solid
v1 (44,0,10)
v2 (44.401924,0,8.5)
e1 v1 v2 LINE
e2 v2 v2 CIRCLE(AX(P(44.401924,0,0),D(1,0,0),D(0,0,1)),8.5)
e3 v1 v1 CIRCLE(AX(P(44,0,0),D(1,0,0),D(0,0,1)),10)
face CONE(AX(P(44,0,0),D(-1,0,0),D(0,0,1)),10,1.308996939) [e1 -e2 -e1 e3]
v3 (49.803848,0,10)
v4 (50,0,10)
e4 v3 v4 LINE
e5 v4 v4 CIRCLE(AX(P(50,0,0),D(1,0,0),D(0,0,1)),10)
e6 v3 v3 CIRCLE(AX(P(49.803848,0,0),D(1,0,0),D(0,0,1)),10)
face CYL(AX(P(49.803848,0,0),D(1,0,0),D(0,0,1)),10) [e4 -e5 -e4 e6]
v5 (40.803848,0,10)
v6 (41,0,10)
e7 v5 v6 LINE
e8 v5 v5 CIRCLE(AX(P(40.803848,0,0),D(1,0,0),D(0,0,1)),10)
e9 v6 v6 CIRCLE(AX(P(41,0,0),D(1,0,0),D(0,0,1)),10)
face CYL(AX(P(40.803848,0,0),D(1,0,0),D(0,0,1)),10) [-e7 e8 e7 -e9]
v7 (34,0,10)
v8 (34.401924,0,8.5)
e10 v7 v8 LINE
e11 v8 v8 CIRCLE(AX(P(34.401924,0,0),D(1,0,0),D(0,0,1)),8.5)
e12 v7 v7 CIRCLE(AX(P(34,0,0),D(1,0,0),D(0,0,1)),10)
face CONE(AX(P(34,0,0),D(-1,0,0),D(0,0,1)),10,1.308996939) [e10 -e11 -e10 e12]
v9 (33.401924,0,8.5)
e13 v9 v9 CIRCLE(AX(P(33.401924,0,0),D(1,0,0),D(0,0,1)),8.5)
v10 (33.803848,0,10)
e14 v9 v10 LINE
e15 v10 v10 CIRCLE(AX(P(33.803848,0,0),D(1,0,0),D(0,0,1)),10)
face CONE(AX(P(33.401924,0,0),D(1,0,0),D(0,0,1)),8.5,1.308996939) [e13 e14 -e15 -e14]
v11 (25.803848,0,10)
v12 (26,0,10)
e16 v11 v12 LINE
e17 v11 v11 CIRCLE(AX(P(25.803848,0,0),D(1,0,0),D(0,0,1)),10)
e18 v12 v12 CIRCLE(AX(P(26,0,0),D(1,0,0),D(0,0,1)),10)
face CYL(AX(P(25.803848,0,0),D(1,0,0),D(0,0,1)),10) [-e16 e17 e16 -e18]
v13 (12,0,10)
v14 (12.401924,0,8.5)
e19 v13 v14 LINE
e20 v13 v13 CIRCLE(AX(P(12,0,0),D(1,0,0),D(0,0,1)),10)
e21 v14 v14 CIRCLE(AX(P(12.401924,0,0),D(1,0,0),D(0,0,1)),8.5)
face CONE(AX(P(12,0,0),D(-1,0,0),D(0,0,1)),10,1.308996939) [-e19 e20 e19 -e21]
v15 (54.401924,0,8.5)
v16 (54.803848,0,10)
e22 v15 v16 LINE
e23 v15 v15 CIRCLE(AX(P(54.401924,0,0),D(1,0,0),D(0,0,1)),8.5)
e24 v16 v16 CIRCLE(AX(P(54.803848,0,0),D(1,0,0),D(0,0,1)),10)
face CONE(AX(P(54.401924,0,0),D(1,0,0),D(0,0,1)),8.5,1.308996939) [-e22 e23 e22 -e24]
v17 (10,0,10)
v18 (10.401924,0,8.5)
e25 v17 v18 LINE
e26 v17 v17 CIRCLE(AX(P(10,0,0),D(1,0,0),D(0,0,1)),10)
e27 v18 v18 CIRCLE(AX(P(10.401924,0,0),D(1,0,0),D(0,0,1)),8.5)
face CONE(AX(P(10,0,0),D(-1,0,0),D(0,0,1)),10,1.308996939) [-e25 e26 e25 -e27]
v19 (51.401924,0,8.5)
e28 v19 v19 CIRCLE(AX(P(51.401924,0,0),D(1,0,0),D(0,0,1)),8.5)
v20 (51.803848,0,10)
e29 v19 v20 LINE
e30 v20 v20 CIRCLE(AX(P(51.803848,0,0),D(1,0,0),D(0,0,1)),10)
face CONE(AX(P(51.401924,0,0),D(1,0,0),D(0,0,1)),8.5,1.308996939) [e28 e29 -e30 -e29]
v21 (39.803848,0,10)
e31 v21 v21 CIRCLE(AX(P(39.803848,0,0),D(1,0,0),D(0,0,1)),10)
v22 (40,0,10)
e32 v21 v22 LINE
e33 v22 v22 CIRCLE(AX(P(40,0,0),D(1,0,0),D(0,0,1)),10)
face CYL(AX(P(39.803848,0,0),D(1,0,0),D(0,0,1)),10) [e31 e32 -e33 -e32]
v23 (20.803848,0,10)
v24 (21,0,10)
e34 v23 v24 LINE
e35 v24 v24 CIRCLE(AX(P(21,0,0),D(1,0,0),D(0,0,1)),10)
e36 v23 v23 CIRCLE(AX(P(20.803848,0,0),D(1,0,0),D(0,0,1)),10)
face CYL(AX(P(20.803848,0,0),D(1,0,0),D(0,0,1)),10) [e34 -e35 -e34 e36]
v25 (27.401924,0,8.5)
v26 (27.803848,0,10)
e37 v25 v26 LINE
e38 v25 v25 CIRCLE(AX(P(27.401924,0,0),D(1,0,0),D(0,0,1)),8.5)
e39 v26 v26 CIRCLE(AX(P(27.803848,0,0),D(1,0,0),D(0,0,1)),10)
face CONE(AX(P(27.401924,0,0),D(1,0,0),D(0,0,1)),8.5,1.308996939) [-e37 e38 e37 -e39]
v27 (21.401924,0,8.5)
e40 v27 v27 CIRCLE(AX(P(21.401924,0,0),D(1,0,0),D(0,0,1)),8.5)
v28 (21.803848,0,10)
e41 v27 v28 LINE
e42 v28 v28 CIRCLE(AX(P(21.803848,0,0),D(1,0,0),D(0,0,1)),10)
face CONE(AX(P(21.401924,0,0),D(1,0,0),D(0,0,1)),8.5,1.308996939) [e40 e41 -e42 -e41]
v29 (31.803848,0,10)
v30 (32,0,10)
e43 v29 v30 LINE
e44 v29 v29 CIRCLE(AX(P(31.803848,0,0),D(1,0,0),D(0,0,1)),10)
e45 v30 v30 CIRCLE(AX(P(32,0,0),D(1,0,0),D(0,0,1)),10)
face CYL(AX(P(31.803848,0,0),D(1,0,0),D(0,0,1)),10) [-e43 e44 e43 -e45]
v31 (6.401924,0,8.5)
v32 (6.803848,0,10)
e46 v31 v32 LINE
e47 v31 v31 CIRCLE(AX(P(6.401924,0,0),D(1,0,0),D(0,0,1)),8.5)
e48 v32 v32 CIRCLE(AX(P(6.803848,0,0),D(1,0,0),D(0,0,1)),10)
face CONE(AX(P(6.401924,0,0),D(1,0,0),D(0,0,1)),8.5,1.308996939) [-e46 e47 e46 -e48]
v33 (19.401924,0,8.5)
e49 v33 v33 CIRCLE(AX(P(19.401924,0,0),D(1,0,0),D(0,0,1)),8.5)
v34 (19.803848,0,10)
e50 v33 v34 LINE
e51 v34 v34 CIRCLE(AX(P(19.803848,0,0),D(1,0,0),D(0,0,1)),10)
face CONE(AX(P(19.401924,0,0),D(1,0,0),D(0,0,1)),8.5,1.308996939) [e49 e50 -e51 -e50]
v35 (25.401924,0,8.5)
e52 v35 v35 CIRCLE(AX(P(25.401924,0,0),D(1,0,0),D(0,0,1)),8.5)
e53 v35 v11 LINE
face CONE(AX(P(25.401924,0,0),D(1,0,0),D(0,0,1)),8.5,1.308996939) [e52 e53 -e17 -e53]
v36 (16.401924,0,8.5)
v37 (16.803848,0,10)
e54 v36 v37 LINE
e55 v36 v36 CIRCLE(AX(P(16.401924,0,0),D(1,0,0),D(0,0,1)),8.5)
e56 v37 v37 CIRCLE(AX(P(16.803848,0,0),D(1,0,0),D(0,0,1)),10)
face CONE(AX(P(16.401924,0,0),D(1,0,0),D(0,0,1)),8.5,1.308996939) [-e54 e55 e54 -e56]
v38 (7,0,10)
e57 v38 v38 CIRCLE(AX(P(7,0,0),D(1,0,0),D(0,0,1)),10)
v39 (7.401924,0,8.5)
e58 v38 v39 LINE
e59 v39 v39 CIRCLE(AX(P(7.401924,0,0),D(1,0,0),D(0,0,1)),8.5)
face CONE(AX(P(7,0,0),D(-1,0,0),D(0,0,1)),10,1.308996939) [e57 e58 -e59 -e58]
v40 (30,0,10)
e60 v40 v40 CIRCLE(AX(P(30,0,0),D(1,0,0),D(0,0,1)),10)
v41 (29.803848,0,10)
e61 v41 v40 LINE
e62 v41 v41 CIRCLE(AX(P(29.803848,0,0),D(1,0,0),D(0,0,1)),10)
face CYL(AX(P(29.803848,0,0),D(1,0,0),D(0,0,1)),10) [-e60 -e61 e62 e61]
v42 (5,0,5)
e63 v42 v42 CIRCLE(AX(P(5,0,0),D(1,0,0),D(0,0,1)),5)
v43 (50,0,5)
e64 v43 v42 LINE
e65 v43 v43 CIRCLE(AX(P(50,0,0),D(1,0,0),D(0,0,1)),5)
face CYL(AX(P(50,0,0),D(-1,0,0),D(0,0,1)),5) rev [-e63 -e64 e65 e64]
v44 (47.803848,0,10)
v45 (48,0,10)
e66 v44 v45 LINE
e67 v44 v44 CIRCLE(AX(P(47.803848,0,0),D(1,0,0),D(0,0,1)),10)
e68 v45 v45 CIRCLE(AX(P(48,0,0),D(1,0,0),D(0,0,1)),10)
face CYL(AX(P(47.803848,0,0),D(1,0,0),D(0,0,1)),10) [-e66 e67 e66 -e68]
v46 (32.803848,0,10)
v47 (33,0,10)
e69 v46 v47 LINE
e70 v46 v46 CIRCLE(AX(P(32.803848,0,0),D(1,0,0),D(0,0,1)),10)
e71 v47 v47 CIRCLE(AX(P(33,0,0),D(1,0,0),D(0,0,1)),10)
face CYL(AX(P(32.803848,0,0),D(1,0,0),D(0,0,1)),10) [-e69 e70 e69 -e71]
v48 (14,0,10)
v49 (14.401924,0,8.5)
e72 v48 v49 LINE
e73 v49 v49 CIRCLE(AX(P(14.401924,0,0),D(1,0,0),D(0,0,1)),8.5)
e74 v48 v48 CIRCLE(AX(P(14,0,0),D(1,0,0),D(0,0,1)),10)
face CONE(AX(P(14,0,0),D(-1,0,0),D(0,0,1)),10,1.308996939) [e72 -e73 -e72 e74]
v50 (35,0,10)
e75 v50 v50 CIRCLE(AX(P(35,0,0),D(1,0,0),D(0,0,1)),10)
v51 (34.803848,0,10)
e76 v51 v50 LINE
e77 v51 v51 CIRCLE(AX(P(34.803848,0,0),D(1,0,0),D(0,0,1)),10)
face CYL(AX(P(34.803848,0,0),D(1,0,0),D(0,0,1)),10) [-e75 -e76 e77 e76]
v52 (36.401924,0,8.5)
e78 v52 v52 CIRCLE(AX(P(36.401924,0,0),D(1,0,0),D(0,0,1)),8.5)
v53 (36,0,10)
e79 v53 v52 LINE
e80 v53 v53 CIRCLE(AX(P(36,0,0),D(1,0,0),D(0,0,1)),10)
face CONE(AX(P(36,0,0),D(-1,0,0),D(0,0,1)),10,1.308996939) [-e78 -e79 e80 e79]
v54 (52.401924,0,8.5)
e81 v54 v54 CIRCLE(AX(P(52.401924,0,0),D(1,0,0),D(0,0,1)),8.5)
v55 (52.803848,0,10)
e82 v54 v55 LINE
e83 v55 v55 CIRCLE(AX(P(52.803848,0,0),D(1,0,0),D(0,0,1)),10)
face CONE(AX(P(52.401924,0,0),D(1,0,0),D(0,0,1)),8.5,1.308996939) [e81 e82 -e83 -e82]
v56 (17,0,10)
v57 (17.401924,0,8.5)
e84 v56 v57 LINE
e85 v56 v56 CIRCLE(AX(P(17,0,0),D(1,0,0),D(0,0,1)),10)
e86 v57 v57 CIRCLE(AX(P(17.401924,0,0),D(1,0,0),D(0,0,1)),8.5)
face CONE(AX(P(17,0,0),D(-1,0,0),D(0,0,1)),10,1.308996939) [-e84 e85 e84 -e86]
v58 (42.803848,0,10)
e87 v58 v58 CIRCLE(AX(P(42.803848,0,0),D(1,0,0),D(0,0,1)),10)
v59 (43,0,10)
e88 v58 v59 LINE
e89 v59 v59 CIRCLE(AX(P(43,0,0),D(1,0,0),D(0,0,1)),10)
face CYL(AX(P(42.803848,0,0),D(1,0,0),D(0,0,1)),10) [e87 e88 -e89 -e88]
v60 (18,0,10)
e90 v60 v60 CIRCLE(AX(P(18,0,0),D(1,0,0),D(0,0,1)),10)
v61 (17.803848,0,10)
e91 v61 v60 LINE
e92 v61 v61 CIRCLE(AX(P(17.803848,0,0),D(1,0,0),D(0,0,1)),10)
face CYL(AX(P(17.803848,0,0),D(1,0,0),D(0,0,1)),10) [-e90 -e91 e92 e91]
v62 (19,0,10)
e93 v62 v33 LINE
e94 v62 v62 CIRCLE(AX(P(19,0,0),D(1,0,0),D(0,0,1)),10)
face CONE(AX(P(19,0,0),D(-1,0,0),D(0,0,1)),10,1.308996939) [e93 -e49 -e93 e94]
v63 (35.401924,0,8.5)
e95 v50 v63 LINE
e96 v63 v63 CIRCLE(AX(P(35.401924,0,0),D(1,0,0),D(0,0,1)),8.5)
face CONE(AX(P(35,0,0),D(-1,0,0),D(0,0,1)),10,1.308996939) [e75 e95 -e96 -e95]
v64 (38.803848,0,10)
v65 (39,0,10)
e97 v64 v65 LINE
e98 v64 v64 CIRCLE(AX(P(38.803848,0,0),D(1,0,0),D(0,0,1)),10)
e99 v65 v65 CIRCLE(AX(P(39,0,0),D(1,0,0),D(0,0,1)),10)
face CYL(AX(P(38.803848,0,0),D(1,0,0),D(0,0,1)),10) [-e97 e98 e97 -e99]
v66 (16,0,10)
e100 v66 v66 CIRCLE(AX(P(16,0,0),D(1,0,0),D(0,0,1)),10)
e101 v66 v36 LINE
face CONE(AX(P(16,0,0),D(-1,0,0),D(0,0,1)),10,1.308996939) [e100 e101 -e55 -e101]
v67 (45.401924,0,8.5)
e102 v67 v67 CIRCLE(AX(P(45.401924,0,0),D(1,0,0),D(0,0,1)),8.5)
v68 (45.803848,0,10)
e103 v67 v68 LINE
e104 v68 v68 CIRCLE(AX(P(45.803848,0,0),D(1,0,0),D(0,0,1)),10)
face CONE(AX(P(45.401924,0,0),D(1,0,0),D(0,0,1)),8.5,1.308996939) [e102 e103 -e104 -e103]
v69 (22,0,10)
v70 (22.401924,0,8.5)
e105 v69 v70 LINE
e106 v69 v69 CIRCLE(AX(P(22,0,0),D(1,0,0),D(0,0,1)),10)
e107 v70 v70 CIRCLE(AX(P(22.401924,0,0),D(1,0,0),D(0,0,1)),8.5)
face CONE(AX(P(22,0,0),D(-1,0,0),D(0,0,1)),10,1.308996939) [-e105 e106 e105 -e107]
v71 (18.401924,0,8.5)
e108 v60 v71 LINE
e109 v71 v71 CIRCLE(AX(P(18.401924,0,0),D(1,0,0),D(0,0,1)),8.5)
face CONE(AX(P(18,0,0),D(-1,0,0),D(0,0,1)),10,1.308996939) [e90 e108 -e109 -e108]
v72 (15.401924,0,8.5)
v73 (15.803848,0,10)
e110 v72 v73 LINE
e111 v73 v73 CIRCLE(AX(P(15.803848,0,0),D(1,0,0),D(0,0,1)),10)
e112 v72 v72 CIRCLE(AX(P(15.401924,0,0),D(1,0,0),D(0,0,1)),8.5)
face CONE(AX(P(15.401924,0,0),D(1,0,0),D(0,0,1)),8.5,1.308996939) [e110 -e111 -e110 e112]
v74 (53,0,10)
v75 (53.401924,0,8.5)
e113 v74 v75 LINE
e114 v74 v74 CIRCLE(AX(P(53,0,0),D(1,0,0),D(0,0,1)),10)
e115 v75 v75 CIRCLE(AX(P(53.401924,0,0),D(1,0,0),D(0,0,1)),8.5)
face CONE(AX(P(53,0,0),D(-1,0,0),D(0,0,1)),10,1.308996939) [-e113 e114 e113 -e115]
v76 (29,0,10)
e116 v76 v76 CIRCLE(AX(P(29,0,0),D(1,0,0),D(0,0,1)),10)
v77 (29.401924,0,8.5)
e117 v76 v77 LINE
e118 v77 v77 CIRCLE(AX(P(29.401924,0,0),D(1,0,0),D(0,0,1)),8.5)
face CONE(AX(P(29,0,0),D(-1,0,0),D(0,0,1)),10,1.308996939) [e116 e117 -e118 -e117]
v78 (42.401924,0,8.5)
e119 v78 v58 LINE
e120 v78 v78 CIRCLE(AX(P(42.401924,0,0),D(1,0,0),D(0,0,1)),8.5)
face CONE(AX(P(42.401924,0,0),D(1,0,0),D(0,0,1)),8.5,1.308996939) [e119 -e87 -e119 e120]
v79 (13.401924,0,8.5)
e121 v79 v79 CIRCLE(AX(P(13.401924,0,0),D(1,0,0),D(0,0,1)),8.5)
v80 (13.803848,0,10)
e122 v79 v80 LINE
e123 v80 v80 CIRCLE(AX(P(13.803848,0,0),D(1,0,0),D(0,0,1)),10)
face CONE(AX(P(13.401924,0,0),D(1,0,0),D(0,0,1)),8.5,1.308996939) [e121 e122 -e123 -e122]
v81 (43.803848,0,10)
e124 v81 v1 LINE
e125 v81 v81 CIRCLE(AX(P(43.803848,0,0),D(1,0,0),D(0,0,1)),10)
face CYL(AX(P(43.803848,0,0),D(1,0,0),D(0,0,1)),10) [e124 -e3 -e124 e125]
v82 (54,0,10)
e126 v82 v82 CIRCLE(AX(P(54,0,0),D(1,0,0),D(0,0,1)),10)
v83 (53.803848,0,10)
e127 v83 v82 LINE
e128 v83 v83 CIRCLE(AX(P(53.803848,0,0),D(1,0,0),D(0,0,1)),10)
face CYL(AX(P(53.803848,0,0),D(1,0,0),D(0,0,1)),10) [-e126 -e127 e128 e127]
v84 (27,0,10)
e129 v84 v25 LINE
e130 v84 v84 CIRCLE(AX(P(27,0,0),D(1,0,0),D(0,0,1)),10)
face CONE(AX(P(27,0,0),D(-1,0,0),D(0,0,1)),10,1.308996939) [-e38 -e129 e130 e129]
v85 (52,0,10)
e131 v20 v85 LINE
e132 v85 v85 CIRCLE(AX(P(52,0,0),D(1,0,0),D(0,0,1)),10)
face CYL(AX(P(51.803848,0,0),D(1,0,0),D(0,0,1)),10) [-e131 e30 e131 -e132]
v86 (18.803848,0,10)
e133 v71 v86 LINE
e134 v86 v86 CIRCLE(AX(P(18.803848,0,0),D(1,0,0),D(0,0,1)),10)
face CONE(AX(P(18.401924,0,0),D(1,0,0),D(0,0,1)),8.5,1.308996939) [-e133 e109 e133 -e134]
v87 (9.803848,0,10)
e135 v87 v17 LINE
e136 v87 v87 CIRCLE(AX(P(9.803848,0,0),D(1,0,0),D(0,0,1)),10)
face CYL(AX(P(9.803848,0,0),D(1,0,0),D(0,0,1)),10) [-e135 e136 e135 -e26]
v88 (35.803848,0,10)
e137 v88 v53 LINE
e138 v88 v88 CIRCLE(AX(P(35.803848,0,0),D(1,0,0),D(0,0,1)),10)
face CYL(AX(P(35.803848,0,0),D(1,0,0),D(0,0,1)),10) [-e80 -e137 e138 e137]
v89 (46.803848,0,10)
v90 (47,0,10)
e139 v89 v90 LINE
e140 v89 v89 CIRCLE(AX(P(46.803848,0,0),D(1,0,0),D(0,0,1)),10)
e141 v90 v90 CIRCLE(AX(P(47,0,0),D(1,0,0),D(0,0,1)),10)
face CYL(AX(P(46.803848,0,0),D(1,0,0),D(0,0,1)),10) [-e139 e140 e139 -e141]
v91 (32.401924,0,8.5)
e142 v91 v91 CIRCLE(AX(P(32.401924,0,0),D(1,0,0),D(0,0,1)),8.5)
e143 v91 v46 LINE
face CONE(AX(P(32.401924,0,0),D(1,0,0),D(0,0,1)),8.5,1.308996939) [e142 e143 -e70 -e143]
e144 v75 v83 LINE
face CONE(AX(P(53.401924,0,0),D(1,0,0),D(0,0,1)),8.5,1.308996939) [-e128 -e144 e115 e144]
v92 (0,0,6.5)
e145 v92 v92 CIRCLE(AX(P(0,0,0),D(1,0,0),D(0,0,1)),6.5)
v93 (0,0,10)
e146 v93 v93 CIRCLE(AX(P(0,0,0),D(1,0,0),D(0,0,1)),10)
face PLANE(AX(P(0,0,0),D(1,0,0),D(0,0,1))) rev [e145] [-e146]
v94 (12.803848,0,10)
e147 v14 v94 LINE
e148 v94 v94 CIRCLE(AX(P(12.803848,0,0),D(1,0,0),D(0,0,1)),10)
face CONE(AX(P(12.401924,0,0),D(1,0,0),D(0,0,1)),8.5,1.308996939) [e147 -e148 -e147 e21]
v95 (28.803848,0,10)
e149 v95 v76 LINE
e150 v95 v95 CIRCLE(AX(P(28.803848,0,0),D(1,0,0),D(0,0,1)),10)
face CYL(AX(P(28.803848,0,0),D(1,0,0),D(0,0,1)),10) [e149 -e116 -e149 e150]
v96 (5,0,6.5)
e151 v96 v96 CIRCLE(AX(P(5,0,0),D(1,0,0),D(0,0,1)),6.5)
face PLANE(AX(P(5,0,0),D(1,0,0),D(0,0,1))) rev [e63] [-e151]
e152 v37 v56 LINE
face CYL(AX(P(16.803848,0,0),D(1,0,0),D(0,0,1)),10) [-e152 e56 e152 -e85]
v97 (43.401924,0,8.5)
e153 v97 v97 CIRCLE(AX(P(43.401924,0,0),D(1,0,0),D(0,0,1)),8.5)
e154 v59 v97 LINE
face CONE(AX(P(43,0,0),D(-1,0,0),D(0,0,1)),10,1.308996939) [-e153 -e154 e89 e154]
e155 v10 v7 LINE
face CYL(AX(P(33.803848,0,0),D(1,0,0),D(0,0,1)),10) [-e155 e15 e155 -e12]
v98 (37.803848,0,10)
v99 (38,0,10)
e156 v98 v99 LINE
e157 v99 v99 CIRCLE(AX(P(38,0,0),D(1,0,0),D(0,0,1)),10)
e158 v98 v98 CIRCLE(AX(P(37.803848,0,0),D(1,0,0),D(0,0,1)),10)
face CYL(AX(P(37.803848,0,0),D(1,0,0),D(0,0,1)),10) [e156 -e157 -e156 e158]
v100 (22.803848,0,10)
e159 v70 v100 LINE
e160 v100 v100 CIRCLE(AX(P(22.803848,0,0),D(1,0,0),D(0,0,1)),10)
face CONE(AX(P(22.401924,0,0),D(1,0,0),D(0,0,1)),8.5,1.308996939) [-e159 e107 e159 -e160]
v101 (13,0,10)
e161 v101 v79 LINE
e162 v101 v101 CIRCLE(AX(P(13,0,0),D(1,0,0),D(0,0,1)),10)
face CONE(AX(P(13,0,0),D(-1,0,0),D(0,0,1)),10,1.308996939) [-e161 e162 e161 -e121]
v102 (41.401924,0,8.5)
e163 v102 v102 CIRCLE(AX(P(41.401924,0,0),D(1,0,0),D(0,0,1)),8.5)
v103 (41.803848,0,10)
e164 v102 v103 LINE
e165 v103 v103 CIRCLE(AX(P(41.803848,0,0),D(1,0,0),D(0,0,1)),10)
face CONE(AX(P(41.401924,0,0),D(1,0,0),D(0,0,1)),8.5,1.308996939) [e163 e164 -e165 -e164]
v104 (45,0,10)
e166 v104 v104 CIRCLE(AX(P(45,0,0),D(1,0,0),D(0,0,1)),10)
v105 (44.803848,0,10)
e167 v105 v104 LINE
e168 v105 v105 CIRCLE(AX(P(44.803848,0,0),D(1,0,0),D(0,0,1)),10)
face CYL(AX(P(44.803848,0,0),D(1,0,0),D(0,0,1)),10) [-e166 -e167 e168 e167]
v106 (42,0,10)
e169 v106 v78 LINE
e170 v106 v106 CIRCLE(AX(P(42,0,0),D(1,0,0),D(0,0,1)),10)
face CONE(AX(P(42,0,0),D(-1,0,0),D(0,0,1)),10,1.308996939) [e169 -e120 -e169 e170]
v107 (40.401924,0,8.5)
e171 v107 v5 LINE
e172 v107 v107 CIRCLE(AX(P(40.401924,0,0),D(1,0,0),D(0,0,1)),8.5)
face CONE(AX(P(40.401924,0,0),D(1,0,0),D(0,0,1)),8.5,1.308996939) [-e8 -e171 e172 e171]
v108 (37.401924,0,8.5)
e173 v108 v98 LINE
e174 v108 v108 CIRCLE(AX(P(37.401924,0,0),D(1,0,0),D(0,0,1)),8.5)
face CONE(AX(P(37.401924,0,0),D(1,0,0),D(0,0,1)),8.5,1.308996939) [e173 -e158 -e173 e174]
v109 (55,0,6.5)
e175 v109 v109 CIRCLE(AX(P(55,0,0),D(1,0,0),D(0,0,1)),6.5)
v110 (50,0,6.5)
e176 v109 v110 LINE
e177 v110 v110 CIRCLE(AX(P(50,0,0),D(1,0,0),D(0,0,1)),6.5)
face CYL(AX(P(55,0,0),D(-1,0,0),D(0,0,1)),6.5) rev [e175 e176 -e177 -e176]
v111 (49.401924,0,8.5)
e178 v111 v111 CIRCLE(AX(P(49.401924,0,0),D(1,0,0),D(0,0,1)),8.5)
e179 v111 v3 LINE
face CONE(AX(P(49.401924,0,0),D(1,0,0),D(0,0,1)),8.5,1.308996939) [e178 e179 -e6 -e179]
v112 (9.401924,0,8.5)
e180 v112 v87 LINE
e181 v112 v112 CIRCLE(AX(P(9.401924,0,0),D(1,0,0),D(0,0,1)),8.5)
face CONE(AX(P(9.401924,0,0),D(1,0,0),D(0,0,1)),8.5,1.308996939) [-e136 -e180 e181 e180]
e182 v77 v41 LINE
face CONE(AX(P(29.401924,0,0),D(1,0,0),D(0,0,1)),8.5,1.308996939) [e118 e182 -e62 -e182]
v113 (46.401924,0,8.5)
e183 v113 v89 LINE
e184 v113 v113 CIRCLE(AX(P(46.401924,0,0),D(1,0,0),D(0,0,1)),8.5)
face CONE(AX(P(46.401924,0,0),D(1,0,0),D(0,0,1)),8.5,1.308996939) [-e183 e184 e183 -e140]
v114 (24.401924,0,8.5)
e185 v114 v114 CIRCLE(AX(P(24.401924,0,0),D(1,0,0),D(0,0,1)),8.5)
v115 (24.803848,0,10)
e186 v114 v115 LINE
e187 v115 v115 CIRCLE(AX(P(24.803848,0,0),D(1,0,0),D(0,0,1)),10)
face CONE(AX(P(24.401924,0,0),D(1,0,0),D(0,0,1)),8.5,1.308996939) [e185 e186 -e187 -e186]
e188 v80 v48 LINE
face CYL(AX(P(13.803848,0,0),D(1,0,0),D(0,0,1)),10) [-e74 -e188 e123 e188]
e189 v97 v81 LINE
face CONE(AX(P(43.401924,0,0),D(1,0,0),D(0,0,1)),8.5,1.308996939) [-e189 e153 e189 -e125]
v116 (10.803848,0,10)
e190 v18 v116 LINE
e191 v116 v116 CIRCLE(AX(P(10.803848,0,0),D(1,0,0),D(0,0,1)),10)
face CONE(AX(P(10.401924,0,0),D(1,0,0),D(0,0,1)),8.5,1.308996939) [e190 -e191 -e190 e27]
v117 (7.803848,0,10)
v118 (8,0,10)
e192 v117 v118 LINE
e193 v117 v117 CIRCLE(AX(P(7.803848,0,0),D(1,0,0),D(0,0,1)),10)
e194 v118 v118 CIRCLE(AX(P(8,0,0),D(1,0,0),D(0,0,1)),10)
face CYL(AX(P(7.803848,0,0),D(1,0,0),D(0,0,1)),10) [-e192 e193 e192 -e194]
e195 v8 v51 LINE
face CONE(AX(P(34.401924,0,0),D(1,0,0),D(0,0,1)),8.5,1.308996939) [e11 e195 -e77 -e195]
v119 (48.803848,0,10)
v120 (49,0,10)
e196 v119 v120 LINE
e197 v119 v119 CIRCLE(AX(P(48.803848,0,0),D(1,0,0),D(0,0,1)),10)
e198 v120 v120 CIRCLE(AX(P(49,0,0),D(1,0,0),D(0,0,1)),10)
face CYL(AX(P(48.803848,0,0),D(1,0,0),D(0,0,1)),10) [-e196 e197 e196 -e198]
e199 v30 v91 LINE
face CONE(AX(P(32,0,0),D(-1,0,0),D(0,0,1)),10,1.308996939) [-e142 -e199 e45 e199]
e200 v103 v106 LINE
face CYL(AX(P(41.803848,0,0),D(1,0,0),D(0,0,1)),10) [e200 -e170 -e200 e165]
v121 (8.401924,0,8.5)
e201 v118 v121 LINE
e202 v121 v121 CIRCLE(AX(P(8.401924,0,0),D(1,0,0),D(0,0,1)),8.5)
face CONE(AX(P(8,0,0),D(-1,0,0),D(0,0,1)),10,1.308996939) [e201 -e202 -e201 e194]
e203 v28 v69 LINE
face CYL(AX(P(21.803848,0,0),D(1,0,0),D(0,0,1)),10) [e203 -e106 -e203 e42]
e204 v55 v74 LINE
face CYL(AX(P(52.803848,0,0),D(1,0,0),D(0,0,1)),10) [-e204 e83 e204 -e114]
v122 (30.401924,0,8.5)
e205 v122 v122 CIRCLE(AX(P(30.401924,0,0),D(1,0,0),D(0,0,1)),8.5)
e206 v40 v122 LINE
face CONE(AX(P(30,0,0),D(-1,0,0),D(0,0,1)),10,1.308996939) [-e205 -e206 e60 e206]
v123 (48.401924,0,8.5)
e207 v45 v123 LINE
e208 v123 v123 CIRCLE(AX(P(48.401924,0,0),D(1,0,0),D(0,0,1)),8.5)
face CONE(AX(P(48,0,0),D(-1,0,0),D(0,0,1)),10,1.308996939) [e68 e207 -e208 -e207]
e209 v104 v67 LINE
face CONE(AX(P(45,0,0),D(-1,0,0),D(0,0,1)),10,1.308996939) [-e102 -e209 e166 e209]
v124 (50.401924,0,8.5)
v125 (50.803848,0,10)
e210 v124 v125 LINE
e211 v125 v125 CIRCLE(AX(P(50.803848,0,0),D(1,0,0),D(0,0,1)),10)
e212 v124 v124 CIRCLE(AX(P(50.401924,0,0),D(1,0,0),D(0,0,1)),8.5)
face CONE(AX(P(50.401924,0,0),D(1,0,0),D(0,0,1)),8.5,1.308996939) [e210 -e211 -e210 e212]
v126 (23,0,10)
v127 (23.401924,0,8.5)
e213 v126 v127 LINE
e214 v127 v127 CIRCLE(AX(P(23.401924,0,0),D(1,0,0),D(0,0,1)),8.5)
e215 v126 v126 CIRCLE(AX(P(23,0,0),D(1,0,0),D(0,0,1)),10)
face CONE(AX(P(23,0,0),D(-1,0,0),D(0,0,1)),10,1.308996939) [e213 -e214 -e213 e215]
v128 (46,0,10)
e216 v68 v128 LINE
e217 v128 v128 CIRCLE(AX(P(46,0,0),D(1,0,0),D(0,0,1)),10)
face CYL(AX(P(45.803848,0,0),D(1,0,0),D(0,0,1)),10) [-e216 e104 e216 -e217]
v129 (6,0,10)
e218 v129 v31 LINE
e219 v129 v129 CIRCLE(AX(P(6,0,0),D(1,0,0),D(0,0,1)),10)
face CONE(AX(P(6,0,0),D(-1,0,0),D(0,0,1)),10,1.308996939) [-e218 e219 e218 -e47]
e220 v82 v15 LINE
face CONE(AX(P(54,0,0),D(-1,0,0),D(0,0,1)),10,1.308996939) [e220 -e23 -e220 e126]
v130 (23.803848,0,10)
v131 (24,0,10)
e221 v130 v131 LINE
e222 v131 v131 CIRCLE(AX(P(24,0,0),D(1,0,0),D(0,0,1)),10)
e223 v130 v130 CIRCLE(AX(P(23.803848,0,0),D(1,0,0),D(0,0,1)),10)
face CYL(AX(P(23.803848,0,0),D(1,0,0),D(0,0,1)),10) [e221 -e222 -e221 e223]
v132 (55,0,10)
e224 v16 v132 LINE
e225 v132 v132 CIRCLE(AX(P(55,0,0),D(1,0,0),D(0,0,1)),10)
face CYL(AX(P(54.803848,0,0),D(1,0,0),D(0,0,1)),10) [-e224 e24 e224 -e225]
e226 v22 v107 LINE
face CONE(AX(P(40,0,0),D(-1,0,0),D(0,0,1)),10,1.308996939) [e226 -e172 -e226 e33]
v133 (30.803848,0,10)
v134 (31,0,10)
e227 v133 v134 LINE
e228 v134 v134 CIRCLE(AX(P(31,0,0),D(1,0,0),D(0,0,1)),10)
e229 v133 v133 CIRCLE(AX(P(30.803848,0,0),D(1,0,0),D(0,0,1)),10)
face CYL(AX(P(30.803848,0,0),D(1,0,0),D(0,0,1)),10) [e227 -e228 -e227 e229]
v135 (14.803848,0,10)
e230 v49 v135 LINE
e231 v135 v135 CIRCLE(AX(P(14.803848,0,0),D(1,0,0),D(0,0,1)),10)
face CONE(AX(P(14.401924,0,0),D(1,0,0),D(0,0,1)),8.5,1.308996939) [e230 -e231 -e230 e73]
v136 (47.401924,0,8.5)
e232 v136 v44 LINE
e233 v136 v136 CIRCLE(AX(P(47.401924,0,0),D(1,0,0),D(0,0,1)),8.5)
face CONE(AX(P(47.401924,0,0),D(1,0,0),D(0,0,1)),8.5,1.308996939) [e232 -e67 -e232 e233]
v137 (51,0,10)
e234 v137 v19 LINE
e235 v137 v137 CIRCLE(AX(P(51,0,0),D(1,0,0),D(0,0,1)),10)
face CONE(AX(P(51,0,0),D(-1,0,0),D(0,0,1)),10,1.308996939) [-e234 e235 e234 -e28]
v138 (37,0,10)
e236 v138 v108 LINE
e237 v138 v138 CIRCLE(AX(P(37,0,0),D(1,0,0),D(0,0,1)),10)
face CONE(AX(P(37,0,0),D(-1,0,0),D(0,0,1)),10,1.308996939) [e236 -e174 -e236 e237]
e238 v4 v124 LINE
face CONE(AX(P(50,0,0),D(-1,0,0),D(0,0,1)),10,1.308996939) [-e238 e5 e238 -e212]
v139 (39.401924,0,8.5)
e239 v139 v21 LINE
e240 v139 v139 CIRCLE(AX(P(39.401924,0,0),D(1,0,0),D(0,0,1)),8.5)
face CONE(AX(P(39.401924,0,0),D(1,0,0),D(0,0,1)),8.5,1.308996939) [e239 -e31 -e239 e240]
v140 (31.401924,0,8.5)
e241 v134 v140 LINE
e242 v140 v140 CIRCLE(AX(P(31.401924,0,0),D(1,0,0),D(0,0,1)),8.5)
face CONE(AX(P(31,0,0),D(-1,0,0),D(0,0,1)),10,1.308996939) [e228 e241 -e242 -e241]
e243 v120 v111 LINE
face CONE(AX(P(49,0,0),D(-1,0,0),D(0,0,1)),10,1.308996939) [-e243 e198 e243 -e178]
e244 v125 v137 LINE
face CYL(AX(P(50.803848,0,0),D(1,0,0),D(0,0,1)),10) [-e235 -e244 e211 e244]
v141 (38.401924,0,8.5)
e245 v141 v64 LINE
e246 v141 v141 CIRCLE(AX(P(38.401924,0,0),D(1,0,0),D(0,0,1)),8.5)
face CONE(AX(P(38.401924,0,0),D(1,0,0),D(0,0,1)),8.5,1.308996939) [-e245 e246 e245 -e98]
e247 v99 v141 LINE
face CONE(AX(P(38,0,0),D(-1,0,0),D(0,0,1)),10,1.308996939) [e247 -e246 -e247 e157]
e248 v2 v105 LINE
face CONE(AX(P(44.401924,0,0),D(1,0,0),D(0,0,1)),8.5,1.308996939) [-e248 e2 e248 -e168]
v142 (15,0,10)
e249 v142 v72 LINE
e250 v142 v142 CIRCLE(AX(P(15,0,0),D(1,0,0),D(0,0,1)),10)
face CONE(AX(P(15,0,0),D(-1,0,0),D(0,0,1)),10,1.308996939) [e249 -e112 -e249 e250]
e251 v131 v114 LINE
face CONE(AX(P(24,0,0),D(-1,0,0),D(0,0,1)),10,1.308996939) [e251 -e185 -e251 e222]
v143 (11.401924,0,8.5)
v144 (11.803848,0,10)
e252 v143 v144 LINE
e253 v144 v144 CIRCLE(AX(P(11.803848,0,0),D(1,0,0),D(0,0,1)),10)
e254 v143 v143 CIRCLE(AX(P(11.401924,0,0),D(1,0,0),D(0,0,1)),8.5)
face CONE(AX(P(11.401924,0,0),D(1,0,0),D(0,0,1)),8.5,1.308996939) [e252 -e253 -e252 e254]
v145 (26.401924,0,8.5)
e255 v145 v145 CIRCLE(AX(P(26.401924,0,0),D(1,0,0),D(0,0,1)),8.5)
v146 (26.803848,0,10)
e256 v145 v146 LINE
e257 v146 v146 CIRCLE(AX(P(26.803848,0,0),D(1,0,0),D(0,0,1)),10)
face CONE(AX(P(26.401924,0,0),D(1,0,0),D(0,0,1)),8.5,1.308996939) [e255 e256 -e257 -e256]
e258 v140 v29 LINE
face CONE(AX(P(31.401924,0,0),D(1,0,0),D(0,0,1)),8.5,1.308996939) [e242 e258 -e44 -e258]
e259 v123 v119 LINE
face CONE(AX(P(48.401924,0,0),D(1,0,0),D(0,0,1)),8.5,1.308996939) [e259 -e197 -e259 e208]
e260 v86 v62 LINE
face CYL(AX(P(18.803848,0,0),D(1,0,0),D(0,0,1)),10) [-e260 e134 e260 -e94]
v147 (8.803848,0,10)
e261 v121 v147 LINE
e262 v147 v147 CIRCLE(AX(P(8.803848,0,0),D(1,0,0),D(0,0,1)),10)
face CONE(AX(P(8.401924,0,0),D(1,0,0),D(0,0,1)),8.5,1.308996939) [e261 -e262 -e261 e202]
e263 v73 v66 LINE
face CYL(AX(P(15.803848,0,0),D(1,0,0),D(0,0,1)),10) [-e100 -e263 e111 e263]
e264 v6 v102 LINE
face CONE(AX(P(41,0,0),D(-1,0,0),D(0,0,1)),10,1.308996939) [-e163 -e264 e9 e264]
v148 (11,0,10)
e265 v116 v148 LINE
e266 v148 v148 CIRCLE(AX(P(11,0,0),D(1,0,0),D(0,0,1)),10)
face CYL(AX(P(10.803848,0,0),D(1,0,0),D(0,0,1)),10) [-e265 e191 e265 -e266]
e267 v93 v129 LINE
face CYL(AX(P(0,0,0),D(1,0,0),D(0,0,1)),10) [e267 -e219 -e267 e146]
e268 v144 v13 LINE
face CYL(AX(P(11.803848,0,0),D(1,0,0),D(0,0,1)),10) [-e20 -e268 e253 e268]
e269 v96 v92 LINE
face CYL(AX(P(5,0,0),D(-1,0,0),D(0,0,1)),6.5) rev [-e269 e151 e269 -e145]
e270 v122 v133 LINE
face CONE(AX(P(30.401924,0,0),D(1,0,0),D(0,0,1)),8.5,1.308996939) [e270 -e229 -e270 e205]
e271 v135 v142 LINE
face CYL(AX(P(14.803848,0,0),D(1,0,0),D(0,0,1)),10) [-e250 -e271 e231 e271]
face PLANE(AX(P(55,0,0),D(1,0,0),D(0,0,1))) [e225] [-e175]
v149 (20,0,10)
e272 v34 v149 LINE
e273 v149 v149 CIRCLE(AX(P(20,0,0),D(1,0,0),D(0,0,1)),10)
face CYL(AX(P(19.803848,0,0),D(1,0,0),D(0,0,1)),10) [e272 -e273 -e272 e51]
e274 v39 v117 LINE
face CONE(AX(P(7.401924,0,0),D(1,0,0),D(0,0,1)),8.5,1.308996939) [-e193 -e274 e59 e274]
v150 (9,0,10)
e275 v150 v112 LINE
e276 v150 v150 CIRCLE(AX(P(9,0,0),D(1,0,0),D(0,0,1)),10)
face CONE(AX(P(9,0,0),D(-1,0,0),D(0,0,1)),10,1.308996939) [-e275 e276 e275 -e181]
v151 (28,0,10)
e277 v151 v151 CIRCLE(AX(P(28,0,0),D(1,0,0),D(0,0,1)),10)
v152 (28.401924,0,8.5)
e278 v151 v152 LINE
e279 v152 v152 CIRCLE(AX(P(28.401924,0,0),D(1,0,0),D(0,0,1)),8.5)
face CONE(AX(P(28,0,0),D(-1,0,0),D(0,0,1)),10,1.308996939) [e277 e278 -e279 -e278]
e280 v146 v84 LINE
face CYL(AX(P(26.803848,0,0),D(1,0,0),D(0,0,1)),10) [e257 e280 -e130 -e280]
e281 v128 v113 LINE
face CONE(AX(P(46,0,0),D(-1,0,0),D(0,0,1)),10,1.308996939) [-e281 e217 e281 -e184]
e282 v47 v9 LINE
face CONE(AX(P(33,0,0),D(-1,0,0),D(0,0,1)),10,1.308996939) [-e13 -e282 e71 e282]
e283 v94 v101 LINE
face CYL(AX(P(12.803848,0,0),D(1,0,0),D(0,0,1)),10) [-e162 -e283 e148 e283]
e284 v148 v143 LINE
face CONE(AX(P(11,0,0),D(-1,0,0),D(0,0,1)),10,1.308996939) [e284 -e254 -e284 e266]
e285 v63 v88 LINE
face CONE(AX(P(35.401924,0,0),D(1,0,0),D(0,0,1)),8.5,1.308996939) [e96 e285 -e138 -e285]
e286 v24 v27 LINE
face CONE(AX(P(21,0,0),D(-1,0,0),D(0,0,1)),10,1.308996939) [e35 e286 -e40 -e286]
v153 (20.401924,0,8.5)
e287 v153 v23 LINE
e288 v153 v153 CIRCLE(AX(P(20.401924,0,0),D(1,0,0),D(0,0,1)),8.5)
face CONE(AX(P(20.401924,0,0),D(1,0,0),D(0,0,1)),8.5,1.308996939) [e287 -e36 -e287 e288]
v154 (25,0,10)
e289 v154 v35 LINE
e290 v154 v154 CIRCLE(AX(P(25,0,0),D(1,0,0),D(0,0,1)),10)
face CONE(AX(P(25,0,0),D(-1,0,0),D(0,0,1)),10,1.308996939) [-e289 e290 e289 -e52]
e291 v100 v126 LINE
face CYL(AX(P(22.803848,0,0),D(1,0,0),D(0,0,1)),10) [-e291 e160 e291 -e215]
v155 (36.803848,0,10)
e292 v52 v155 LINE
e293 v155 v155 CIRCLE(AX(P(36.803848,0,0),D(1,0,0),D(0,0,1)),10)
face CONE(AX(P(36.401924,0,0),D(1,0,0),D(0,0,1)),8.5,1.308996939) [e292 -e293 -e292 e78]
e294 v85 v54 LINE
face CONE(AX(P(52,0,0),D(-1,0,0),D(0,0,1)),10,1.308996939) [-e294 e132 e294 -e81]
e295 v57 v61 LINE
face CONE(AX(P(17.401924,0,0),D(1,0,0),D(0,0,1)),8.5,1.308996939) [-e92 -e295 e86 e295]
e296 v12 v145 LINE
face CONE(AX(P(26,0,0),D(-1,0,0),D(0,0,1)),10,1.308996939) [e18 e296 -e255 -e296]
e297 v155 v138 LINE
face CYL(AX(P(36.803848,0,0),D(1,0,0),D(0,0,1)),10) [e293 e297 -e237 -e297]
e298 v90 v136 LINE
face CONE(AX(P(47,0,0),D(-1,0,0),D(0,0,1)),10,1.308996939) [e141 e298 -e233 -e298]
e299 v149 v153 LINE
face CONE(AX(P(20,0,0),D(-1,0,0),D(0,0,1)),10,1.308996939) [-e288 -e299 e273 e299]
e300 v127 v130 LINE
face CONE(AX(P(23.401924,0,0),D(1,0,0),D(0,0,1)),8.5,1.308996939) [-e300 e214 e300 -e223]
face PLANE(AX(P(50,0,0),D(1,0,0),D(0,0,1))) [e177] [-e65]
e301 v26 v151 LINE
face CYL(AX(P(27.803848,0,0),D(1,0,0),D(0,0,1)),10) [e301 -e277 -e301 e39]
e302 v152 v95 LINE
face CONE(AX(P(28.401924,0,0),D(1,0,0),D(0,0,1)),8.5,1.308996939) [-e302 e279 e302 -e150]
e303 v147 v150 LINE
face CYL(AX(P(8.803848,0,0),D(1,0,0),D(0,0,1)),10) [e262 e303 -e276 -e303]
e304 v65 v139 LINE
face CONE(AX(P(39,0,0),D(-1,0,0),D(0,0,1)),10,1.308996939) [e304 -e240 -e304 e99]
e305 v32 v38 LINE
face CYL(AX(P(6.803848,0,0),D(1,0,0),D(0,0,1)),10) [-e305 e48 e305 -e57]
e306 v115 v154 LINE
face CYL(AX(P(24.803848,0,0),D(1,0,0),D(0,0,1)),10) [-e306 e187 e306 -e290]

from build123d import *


with BuildPart() as part:
    # Sketch1 → Revolve1 (revolve)
    with BuildSketch(Plane.XY, mode=Mode.PRIVATE) as revolve1_sk:
        Polygon((0, 6.5), (0, 10), (6, 10), (6.401923789, 8.5), (6.803847577, 10), (7, 10), (7.401923789, 8.5), (7.803847577, 10), (8, 10), (8.401923789, 8.5), (8.803847577, 10), (9, 10), (9.401923789, 8.5), (9.803847577, 10), (10, 10), (10.401923789, 8.5), (10.803847577, 10), (11, 10), (11.401923789, 8.5), (11.803847577, 10), (12, 10), (12.401923789, 8.5), (12.803847577, 10), (13, 10), (13.401923789, 8.5), (13.803847577, 10), (14, 10), (14.401923789, 8.5), (14.803847577, 10), (15, 10), (15.401923789, 8.5), (15.803847577, 10), (16, 10), (16.401923789, 8.5), (16.803847577, 10), (17, 10), (17.401923789, 8.5), (17.803847577, 10), (18, 10), (18.401923789, 8.5), (18.803847577, 10), (19, 10), (19.401923789, 8.5), (19.803847577, 10), (20, 10), (20.401923789, 8.5), (20.803847577, 10), (21, 10), (21.401923789, 8.5), (21.803847577, 10), (22, 10), (22.401923789, 8.5), (22.803847577, 10), (23, 10), (23.401923789, 8.5), (23.803847577, 10), (24, 10), (24.401923789, 8.5), (24.803847577, 10), (25, 10), (25.401923789, 8.5), (25.803847577, 10), (26, 10), (26.401923789, 8.5), (26.803847577, 10), (27, 10), (27.401923789, 8.5), (27.803847577, 10), (28, 10), (28.401923789, 8.5), (28.803847577, 10), (29, 10), (29.401923789, 8.5), (29.803847577, 10), (30, 10), (30.401923789, 8.5), (30.803847577, 10), (31, 10), (31.401923789, 8.5), (31.803847577, 10), (32, 10), (32.401923789, 8.5), (32.803847577, 10), (33, 10), (33.401923789, 8.5), (33.803847577, 10), (34, 10), (34.401923789, 8.5), (34.803847577, 10), (35, 10), (35.401923789, 8.5), (35.803847577, 10), (36, 10), (36.401923789, 8.5), (36.803847577, 10), (37, 10), (37.401923789, 8.5), (37.803847577, 10), (38, 10), (38.401923789, 8.5), (38.803847577, 10), (39, 10), (39.401923789, 8.5), (39.803847577, 10), (40, 10), (40.401923789, 8.5), (40.803847577, 10), (41, 10), (41.401923789, 8.5), (41.803847577, 10), (42, 10), (42.401923789, 8.5), (42.803847577, 10), (43, 10), (43.401923789, 8.5), (43.803847577, 10), (44, 10), (44.401923789, 8.5), (44.803847577, 10), (45, 10), (45.401923789, 8.5), (45.803847577, 10), (46, 10), (46.401923789, 8.5), (46.803847577, 10), (47, 10), (47.401923789, 8.5), (47.803847577, 10), (48, 10), (48.401923789, 8.5), (48.803847577, 10), (49, 10), (49.401923789, 8.5), (49.803847577, 10), (50, 10), (50.401923789, 8.5), (50.803847577, 10), (51, 10), (51.401923789, 8.5), (51.803847577, 10), (52, 10), (52.401923789, 8.5), (52.803847577, 10), (53, 10), (53.401923789, 8.5), (53.803847577, 10), (54, 10), (54.401923789, 8.5), (54.803847577, 10), (55, 10), (55, 6.5), (50, 6.5), (50, 5), (5, 5), (5, 6.5), align=None)
    revolve(revolve1_sk.sketch.rotate(Axis((0, 0, 0), (1, 0, 0)), 90), axis=Axis((0, 0, 0), (1, 0, 0)))


solid = part.part
